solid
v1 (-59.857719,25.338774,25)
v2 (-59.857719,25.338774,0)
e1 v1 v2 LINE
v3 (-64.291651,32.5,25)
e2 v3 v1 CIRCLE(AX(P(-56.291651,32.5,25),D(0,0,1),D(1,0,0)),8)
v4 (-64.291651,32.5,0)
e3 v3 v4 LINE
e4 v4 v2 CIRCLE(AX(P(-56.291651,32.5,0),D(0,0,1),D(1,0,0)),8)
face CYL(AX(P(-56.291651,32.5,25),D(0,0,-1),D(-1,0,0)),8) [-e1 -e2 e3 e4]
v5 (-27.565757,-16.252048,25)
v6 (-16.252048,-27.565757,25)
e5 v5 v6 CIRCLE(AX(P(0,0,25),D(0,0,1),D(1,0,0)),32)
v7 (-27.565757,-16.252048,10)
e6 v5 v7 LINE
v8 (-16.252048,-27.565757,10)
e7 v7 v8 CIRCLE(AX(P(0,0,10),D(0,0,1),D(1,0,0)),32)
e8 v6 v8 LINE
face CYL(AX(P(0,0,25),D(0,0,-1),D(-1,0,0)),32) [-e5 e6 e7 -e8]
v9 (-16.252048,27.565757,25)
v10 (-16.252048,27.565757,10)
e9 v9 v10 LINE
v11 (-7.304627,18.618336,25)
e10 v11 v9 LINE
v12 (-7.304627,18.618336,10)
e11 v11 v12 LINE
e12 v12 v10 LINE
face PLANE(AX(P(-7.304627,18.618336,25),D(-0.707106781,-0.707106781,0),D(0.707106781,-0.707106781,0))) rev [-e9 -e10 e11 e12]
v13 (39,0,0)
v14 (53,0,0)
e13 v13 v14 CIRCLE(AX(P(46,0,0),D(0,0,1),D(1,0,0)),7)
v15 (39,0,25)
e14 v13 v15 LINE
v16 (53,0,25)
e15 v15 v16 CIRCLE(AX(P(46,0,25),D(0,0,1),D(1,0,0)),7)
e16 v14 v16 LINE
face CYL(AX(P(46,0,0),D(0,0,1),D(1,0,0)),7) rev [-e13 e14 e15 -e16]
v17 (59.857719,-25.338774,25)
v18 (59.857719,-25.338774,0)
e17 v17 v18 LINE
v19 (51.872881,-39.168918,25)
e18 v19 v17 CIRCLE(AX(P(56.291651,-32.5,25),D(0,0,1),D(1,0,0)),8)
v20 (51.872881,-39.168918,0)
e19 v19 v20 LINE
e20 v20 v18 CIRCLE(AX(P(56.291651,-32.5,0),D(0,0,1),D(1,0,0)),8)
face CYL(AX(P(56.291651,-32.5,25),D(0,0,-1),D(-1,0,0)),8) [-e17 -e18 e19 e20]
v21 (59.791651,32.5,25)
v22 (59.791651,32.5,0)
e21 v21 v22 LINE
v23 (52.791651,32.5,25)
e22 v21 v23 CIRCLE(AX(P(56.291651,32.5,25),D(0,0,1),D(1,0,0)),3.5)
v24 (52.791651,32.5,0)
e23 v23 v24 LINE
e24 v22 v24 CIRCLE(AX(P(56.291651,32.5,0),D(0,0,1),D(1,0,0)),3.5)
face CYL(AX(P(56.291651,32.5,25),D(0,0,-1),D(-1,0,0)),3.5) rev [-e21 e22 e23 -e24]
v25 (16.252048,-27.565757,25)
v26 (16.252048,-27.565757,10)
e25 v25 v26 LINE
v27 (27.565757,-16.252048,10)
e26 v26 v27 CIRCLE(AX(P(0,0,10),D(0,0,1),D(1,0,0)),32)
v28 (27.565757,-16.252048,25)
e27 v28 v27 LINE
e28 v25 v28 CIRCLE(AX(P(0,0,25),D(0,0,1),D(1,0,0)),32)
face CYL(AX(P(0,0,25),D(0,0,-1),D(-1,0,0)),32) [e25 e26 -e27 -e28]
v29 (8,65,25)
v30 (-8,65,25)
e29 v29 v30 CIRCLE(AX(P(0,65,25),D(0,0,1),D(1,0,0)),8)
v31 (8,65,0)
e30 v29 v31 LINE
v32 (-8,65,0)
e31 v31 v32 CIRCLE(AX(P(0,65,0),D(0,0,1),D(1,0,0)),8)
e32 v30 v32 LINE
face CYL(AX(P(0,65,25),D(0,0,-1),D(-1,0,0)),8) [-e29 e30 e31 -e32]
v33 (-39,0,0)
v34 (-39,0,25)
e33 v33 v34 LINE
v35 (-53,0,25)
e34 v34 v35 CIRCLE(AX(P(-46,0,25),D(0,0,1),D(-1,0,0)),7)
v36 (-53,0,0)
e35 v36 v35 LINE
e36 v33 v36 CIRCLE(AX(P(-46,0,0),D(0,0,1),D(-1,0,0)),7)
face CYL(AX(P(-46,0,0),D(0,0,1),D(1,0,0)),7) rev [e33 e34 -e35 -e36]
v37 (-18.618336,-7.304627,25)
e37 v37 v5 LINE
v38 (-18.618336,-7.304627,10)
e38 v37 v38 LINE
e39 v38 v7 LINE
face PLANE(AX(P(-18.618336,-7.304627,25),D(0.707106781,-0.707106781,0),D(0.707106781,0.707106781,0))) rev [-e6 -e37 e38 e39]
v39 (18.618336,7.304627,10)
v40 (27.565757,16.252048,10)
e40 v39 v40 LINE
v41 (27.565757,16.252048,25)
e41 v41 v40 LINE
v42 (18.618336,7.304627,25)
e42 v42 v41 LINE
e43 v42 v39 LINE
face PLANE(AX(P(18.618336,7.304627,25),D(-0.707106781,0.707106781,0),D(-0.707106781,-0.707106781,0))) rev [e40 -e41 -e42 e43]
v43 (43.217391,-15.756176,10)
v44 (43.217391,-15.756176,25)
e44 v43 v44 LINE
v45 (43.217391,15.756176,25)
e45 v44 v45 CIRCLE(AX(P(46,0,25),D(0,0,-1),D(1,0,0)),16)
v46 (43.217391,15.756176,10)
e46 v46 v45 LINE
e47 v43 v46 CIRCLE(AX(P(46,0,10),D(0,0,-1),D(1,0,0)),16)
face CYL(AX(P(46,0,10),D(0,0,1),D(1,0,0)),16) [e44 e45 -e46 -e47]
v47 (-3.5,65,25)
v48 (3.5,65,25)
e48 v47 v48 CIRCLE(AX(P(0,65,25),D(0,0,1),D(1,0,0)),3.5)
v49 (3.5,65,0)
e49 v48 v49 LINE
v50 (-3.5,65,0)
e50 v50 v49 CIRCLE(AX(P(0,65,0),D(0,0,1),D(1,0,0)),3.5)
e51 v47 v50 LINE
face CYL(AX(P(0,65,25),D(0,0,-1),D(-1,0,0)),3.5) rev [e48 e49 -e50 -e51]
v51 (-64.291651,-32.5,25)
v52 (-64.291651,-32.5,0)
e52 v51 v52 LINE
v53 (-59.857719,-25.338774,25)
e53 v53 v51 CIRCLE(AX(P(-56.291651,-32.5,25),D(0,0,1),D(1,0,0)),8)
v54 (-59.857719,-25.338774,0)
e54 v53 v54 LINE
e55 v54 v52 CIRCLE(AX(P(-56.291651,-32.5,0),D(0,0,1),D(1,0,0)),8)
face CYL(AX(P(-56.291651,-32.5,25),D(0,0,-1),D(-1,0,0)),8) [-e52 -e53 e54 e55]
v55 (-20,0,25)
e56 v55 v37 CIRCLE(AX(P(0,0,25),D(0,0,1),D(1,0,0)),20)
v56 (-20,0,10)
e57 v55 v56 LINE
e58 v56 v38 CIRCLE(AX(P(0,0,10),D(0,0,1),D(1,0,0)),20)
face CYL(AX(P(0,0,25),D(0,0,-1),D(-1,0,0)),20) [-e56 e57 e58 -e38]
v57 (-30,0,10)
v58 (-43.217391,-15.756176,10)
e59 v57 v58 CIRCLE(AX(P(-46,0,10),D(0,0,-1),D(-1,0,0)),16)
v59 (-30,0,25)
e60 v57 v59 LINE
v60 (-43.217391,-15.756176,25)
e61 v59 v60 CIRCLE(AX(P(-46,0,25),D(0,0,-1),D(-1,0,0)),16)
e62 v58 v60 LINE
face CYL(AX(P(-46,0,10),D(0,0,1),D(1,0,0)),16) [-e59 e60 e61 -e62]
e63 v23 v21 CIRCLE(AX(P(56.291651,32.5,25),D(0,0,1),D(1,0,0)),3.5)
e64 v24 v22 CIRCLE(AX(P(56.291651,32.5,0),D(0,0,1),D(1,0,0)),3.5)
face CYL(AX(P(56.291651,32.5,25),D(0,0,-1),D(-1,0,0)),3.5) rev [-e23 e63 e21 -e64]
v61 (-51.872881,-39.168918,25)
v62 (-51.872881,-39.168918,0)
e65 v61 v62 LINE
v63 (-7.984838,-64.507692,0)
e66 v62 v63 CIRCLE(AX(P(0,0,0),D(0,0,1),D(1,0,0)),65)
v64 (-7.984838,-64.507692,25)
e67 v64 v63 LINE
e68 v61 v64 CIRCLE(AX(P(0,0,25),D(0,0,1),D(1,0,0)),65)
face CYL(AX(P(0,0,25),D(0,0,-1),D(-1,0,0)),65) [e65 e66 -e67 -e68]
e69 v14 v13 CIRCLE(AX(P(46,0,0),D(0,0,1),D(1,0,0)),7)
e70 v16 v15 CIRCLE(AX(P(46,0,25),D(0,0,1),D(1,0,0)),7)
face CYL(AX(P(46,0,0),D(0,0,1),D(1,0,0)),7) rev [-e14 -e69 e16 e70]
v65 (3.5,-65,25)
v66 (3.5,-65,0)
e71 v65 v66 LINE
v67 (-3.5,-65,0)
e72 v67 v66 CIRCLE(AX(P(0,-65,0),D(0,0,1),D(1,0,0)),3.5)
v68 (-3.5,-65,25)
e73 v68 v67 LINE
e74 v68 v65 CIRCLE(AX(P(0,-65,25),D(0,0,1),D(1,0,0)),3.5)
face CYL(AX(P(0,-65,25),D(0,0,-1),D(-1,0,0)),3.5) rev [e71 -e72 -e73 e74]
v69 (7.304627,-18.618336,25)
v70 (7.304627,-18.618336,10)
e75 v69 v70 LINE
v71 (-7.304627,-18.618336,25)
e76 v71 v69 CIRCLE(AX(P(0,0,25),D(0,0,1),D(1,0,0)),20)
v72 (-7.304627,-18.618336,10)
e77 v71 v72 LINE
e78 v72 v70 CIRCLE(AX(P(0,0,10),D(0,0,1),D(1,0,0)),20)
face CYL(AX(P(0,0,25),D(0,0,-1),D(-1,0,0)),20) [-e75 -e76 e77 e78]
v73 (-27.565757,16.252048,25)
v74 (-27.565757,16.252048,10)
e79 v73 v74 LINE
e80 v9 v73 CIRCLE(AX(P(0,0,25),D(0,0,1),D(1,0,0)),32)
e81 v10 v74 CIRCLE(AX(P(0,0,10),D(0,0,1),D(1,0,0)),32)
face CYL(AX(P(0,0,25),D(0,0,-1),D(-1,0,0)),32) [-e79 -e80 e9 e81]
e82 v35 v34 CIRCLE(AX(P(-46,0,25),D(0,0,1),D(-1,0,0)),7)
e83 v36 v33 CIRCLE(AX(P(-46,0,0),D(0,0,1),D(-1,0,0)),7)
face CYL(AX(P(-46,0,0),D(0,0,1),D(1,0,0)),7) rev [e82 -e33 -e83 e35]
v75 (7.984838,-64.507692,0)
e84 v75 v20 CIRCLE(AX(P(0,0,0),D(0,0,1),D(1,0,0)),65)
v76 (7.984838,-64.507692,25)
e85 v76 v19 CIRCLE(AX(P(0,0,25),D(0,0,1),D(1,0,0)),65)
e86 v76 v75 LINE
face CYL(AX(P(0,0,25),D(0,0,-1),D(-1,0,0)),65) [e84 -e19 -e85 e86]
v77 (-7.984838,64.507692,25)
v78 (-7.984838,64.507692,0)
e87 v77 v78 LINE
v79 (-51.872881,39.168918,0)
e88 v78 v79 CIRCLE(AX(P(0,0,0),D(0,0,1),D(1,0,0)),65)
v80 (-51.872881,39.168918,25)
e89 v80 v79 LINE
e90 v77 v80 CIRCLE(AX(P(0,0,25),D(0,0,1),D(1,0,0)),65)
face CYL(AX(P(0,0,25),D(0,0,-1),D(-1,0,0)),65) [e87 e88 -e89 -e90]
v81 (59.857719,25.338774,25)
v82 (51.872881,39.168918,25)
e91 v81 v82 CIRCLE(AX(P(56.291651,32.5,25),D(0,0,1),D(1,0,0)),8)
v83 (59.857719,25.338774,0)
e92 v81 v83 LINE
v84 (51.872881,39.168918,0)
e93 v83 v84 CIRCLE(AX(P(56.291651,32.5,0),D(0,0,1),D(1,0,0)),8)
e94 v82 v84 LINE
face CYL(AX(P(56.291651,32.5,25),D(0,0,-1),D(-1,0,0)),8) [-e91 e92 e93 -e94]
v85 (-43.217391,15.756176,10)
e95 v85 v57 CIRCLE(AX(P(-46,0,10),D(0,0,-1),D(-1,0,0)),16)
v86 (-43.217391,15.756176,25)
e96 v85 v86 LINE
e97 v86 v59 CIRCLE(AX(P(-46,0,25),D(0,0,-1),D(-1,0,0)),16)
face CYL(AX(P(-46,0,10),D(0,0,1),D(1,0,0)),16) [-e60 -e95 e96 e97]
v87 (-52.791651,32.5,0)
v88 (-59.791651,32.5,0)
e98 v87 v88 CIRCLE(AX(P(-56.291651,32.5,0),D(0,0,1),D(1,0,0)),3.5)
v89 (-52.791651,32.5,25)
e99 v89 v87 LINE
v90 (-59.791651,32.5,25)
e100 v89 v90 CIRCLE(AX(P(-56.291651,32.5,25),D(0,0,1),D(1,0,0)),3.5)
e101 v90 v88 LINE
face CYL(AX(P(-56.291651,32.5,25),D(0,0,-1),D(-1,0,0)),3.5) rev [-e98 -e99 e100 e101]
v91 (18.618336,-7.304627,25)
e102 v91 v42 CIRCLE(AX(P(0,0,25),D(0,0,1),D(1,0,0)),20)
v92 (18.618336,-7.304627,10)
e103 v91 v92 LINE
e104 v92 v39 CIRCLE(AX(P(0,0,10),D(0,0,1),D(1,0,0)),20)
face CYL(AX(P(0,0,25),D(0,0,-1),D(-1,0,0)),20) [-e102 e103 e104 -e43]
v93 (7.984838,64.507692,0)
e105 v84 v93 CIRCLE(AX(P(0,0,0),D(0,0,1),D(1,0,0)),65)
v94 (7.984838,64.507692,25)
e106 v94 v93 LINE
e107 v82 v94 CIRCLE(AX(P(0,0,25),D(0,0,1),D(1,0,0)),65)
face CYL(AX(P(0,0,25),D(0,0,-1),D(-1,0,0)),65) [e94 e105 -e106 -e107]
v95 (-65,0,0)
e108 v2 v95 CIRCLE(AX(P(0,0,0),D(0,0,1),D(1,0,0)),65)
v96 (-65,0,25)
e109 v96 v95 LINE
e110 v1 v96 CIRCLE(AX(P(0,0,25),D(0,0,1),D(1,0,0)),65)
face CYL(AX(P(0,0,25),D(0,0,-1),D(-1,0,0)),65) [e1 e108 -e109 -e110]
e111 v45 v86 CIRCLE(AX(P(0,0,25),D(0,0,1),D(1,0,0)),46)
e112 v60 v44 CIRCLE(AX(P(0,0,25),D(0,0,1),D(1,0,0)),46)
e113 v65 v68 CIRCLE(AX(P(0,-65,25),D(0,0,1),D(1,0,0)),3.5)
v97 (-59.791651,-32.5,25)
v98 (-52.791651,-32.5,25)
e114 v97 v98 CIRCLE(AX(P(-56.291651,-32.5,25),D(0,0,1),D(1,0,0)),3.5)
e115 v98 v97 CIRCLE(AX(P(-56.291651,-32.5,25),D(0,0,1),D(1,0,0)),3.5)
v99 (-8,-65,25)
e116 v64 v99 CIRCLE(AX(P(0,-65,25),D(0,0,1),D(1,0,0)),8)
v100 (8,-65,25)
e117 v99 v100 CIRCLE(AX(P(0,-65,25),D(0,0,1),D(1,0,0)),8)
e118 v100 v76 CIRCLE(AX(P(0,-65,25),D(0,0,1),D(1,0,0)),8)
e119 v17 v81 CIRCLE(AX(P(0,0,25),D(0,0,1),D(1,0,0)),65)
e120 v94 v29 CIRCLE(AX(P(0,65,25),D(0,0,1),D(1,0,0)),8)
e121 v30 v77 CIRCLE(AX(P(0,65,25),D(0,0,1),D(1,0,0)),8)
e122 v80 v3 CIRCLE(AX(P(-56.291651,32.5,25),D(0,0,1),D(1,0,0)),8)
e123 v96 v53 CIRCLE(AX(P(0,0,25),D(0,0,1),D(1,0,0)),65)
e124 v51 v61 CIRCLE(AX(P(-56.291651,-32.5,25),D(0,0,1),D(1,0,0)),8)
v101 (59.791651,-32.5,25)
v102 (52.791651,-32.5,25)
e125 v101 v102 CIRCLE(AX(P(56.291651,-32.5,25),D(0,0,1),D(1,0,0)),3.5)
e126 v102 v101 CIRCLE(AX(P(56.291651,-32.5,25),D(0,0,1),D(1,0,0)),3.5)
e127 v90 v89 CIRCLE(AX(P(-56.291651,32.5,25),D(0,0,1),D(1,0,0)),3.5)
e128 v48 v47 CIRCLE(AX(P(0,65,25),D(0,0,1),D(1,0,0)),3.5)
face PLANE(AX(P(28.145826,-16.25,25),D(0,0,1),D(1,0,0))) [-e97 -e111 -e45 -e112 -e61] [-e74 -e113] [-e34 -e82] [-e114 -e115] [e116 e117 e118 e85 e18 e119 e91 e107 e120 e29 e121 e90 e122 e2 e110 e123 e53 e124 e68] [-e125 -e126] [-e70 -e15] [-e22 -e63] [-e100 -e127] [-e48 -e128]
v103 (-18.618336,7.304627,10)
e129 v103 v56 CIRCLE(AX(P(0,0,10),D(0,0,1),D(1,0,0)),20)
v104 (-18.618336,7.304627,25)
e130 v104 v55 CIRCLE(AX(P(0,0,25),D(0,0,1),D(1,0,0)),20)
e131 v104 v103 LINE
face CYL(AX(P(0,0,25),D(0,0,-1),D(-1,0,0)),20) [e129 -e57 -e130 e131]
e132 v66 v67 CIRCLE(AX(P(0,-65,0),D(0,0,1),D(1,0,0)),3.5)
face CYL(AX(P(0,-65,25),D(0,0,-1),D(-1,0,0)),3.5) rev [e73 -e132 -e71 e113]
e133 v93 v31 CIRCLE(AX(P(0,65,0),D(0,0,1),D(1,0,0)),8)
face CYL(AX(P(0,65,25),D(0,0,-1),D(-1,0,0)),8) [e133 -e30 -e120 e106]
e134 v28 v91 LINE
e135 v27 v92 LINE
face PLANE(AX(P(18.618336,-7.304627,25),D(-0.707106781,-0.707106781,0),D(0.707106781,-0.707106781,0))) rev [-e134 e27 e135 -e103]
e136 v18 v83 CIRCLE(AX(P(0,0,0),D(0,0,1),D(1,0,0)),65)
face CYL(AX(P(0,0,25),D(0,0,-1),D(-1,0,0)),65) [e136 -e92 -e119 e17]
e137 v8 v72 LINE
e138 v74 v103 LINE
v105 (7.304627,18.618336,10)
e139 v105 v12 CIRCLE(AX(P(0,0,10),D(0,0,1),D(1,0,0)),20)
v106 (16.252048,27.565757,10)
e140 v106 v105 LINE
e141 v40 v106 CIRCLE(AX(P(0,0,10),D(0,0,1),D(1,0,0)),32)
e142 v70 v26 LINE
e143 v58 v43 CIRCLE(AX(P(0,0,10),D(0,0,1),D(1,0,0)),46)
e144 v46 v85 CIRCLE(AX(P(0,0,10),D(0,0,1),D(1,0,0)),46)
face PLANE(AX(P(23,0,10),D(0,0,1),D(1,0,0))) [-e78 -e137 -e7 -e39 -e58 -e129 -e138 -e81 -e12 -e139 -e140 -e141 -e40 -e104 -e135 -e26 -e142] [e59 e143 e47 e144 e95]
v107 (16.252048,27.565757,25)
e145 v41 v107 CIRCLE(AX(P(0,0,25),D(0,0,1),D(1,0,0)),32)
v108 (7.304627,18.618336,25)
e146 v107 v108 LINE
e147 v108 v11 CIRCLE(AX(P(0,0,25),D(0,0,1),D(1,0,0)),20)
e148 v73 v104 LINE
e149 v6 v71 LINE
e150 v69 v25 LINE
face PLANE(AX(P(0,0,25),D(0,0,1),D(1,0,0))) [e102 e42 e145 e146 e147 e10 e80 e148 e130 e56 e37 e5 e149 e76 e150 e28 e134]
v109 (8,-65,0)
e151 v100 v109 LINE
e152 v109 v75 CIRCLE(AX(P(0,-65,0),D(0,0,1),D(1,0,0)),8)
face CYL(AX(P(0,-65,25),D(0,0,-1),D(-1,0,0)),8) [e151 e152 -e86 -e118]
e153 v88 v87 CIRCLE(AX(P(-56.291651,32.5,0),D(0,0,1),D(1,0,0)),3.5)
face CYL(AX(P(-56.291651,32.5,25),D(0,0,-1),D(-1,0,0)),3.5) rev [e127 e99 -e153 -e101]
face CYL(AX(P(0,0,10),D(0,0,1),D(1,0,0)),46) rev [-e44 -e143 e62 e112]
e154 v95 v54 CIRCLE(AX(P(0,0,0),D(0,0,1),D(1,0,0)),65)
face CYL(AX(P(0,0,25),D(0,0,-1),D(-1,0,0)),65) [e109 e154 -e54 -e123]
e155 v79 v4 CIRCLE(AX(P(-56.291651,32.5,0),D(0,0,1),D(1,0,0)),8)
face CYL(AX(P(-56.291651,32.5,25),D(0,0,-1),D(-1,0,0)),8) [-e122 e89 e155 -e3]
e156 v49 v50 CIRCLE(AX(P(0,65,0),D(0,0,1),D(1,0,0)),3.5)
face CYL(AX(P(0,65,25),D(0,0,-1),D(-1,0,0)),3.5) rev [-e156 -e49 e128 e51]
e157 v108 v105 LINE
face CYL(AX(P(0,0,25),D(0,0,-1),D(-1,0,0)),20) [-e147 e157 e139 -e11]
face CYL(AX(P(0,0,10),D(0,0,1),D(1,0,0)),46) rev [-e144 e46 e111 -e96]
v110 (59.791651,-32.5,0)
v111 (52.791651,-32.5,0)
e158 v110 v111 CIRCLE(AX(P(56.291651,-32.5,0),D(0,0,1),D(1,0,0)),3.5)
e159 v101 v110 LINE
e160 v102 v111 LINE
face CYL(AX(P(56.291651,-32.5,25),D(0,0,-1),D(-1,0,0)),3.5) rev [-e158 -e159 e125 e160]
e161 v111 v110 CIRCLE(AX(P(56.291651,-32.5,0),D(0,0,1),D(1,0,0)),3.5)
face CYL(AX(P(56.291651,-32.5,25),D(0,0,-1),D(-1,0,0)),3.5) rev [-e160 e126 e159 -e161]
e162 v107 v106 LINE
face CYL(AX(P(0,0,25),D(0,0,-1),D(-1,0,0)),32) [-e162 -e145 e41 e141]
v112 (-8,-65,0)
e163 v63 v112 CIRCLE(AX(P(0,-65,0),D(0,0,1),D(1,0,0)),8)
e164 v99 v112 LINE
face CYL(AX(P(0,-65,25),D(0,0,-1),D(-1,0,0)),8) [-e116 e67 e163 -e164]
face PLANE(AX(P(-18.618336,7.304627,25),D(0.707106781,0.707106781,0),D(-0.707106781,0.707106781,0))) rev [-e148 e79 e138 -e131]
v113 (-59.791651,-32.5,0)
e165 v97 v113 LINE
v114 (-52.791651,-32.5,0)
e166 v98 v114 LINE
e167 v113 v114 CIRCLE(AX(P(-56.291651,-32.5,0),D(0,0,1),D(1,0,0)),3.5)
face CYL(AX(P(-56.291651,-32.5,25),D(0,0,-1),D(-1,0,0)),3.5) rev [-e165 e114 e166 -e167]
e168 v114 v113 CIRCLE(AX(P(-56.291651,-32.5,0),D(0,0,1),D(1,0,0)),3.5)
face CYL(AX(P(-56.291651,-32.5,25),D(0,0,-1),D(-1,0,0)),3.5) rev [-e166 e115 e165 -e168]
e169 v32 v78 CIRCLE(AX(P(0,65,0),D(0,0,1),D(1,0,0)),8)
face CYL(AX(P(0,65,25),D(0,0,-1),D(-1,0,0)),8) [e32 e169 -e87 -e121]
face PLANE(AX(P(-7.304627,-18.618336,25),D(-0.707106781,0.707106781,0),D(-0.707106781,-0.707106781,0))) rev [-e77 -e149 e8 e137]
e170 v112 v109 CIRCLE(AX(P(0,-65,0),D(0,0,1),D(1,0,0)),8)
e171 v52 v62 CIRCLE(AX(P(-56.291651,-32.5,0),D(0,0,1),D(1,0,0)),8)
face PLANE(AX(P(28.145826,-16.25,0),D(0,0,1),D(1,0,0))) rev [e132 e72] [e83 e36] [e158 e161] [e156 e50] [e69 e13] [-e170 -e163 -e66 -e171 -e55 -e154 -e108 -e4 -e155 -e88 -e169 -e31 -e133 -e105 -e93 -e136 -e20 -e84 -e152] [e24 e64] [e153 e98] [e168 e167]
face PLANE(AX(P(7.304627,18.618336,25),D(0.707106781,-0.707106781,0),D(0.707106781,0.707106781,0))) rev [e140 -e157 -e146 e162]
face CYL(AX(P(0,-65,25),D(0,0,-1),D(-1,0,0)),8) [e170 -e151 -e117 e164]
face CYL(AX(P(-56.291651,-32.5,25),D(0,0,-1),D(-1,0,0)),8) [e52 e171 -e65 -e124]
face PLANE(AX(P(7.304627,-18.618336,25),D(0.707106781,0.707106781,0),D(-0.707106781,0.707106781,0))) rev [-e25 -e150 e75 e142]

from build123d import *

# Parameters (mm, degrees)
FLANGE_PROFILE_SKETCH_R   = 3.5
FLANGE_BODY_25MM_DEPTH    = 25
THROUGH_HOLES_SKETCH_R    = 7
THROUGH_HOLES_DEPTH       = 25
ANNULAR_POCKET_15MM_DEPTH = 15
CROSS_HUB_15MM_DEPTH      = 15


with BuildPart() as part:
    # Flange Profile Sketch → Flange Body 25mm (new body)
    with BuildSketch(Plane.XY):
        with BuildLine():
            ThreePointArc((-7.984837703, 64.507692308), (-32.5, 56.291651246), (-51.872881427, 39.168918449))
            ThreePointArc((-51.872881427, 39.168918449), (-63.219854476, 36.5), (-59.857719129, 25.338773858))
            ThreePointArc((-59.857719129, 25.338773858), (-65, 0), (-59.857719129, -25.338773858))
            ThreePointArc((-59.857719129, -25.338773858), (-63.219854476, -36.5), (-51.872881427, -39.168918449))
            ThreePointArc((-51.872881427, -39.168918449), (-32.5, -56.291651246), (-7.984837703, -64.507692308))
            ThreePointArc((-7.984837703, -64.507692308), (0, -73), (7.984837703, -64.507692308))
            ThreePointArc((7.984837703, -64.507692308), (32.5, -56.291651246), (51.872881427, -39.168918449))
            ThreePointArc((51.872881427, -39.168918449), (63.219854476, -36.5), (59.857719129, -25.338773858))
            ThreePointArc((59.857719129, -25.338773858), (65, 0), (59.857719129, 25.338773858))
            ThreePointArc((59.857719129, 25.338773858), (63.219854476, 36.5), (51.872881427, 39.168918449))
            ThreePointArc((51.872881427, 39.168918449), (32.5, 56.291651246), (7.984837703, 64.507692308))
            ThreePointArc((7.984837703, 64.507692308), (0, 73), (-7.984837703, 64.507692308))
        make_face()
        with Locations((0, 65)):
            Circle(FLANGE_PROFILE_SKETCH_R, mode=Mode.SUBTRACT)
        with Locations((56.291651246, 32.5)):
            Circle(FLANGE_PROFILE_SKETCH_R, mode=Mode.SUBTRACT)
        with Locations((56.291651246, -32.5)):
            Circle(FLANGE_PROFILE_SKETCH_R, mode=Mode.SUBTRACT)
        with Locations((0, -65)):
            Circle(FLANGE_PROFILE_SKETCH_R, mode=Mode.SUBTRACT)
        with Locations((-56.291651246, -32.5)):
            Circle(FLANGE_PROFILE_SKETCH_R, mode=Mode.SUBTRACT)
        with Locations((-56.291651246, 32.5)):
            Circle(FLANGE_PROFILE_SKETCH_R, mode=Mode.SUBTRACT)
    extrude(amount=FLANGE_BODY_25MM_DEPTH)

    # Through Holes Sketch → Through Holes (cut)
    with BuildSketch(Plane.XY.offset(25)):
        with Locations((46, 0)):
            Circle(THROUGH_HOLES_SKETCH_R)
        with Locations(Location((-46, 0, 0), (0, 0, 180))):
            Circle(THROUGH_HOLES_SKETCH_R)
    extrude(amount=-THROUGH_HOLES_DEPTH, mode=Mode.SUBTRACT)

    # Annular Pocket Sketch → Annular Pocket 15mm (cut)
    with BuildSketch(Plane.XY.offset(25)):
        with BuildLine():
            ThreePointArc((43.217391304, 15.756176213), (0, 46), (-43.217391304, 15.756176213))
            ThreePointArc((-43.217391304, 15.756176213), (-30, 0), (-43.217391304, -15.756176213))
            ThreePointArc((-43.217391304, -15.756176213), (0, -46), (43.217391304, -15.756176213))
            ThreePointArc((43.217391304, -15.756176213), (30, 0), (43.217391304, 15.756176213))
        make_face()
    extrude(amount=-ANNULAR_POCKET_15MM_DEPTH, mode=Mode.SUBTRACT)

    # Cross Hub Sketch → Cross Hub 15mm (add)
    with BuildSketch(Plane.XY.offset(10)):
        with BuildLine():
            Line((-7.304627147, 18.618335646), (-16.252048051, 27.56575655))
            ThreePointArc((-16.252048051, 27.56575655), (-22.627416998, 22.627416998), (-27.56575655, 16.252048051))
            Line((-27.56575655, 16.252048051), (-18.618335646, 7.304627147))
            ThreePointArc((-18.618335646, 7.304627147), (-20, 0), (-18.618335646, -7.304627147))
            Line((-18.618335646, -7.304627147), (-27.56575655, -16.252048051))
            ThreePointArc((-27.56575655, -16.252048051), (-22.627416998, -22.627416998), (-16.252048051, -27.56575655))
            Line((-16.252048051, -27.56575655), (-7.304627147, -18.618335646))
            ThreePointArc((-7.304627147, -18.618335646), (0, -20), (7.304627147, -18.618335646))
            Line((7.304627147, -18.618335646), (16.252048051, -27.56575655))
            ThreePointArc((16.252048051, -27.56575655), (22.627416998, -22.627416998), (27.56575655, -16.252048051))
            Line((27.56575655, -16.252048051), (18.618335646, -7.304627147))
            ThreePointArc((18.618335646, -7.304627147), (20, 0), (18.618335646, 7.304627147))
            Line((18.618335646, 7.304627147), (27.56575655, 16.252048051))
            ThreePointArc((27.56575655, 16.252048051), (22.627416998, 22.627416998), (16.252048051, 27.56575655))
            Line((16.252048051, 27.56575655), (7.304627147, 18.618335646))
            ThreePointArc((7.304627147, 18.618335646), (0, 20), (-7.304627147, 18.618335646))
        make_face()
    extrude(amount=CROSS_HUB_15MM_DEPTH)


solid = part.part
